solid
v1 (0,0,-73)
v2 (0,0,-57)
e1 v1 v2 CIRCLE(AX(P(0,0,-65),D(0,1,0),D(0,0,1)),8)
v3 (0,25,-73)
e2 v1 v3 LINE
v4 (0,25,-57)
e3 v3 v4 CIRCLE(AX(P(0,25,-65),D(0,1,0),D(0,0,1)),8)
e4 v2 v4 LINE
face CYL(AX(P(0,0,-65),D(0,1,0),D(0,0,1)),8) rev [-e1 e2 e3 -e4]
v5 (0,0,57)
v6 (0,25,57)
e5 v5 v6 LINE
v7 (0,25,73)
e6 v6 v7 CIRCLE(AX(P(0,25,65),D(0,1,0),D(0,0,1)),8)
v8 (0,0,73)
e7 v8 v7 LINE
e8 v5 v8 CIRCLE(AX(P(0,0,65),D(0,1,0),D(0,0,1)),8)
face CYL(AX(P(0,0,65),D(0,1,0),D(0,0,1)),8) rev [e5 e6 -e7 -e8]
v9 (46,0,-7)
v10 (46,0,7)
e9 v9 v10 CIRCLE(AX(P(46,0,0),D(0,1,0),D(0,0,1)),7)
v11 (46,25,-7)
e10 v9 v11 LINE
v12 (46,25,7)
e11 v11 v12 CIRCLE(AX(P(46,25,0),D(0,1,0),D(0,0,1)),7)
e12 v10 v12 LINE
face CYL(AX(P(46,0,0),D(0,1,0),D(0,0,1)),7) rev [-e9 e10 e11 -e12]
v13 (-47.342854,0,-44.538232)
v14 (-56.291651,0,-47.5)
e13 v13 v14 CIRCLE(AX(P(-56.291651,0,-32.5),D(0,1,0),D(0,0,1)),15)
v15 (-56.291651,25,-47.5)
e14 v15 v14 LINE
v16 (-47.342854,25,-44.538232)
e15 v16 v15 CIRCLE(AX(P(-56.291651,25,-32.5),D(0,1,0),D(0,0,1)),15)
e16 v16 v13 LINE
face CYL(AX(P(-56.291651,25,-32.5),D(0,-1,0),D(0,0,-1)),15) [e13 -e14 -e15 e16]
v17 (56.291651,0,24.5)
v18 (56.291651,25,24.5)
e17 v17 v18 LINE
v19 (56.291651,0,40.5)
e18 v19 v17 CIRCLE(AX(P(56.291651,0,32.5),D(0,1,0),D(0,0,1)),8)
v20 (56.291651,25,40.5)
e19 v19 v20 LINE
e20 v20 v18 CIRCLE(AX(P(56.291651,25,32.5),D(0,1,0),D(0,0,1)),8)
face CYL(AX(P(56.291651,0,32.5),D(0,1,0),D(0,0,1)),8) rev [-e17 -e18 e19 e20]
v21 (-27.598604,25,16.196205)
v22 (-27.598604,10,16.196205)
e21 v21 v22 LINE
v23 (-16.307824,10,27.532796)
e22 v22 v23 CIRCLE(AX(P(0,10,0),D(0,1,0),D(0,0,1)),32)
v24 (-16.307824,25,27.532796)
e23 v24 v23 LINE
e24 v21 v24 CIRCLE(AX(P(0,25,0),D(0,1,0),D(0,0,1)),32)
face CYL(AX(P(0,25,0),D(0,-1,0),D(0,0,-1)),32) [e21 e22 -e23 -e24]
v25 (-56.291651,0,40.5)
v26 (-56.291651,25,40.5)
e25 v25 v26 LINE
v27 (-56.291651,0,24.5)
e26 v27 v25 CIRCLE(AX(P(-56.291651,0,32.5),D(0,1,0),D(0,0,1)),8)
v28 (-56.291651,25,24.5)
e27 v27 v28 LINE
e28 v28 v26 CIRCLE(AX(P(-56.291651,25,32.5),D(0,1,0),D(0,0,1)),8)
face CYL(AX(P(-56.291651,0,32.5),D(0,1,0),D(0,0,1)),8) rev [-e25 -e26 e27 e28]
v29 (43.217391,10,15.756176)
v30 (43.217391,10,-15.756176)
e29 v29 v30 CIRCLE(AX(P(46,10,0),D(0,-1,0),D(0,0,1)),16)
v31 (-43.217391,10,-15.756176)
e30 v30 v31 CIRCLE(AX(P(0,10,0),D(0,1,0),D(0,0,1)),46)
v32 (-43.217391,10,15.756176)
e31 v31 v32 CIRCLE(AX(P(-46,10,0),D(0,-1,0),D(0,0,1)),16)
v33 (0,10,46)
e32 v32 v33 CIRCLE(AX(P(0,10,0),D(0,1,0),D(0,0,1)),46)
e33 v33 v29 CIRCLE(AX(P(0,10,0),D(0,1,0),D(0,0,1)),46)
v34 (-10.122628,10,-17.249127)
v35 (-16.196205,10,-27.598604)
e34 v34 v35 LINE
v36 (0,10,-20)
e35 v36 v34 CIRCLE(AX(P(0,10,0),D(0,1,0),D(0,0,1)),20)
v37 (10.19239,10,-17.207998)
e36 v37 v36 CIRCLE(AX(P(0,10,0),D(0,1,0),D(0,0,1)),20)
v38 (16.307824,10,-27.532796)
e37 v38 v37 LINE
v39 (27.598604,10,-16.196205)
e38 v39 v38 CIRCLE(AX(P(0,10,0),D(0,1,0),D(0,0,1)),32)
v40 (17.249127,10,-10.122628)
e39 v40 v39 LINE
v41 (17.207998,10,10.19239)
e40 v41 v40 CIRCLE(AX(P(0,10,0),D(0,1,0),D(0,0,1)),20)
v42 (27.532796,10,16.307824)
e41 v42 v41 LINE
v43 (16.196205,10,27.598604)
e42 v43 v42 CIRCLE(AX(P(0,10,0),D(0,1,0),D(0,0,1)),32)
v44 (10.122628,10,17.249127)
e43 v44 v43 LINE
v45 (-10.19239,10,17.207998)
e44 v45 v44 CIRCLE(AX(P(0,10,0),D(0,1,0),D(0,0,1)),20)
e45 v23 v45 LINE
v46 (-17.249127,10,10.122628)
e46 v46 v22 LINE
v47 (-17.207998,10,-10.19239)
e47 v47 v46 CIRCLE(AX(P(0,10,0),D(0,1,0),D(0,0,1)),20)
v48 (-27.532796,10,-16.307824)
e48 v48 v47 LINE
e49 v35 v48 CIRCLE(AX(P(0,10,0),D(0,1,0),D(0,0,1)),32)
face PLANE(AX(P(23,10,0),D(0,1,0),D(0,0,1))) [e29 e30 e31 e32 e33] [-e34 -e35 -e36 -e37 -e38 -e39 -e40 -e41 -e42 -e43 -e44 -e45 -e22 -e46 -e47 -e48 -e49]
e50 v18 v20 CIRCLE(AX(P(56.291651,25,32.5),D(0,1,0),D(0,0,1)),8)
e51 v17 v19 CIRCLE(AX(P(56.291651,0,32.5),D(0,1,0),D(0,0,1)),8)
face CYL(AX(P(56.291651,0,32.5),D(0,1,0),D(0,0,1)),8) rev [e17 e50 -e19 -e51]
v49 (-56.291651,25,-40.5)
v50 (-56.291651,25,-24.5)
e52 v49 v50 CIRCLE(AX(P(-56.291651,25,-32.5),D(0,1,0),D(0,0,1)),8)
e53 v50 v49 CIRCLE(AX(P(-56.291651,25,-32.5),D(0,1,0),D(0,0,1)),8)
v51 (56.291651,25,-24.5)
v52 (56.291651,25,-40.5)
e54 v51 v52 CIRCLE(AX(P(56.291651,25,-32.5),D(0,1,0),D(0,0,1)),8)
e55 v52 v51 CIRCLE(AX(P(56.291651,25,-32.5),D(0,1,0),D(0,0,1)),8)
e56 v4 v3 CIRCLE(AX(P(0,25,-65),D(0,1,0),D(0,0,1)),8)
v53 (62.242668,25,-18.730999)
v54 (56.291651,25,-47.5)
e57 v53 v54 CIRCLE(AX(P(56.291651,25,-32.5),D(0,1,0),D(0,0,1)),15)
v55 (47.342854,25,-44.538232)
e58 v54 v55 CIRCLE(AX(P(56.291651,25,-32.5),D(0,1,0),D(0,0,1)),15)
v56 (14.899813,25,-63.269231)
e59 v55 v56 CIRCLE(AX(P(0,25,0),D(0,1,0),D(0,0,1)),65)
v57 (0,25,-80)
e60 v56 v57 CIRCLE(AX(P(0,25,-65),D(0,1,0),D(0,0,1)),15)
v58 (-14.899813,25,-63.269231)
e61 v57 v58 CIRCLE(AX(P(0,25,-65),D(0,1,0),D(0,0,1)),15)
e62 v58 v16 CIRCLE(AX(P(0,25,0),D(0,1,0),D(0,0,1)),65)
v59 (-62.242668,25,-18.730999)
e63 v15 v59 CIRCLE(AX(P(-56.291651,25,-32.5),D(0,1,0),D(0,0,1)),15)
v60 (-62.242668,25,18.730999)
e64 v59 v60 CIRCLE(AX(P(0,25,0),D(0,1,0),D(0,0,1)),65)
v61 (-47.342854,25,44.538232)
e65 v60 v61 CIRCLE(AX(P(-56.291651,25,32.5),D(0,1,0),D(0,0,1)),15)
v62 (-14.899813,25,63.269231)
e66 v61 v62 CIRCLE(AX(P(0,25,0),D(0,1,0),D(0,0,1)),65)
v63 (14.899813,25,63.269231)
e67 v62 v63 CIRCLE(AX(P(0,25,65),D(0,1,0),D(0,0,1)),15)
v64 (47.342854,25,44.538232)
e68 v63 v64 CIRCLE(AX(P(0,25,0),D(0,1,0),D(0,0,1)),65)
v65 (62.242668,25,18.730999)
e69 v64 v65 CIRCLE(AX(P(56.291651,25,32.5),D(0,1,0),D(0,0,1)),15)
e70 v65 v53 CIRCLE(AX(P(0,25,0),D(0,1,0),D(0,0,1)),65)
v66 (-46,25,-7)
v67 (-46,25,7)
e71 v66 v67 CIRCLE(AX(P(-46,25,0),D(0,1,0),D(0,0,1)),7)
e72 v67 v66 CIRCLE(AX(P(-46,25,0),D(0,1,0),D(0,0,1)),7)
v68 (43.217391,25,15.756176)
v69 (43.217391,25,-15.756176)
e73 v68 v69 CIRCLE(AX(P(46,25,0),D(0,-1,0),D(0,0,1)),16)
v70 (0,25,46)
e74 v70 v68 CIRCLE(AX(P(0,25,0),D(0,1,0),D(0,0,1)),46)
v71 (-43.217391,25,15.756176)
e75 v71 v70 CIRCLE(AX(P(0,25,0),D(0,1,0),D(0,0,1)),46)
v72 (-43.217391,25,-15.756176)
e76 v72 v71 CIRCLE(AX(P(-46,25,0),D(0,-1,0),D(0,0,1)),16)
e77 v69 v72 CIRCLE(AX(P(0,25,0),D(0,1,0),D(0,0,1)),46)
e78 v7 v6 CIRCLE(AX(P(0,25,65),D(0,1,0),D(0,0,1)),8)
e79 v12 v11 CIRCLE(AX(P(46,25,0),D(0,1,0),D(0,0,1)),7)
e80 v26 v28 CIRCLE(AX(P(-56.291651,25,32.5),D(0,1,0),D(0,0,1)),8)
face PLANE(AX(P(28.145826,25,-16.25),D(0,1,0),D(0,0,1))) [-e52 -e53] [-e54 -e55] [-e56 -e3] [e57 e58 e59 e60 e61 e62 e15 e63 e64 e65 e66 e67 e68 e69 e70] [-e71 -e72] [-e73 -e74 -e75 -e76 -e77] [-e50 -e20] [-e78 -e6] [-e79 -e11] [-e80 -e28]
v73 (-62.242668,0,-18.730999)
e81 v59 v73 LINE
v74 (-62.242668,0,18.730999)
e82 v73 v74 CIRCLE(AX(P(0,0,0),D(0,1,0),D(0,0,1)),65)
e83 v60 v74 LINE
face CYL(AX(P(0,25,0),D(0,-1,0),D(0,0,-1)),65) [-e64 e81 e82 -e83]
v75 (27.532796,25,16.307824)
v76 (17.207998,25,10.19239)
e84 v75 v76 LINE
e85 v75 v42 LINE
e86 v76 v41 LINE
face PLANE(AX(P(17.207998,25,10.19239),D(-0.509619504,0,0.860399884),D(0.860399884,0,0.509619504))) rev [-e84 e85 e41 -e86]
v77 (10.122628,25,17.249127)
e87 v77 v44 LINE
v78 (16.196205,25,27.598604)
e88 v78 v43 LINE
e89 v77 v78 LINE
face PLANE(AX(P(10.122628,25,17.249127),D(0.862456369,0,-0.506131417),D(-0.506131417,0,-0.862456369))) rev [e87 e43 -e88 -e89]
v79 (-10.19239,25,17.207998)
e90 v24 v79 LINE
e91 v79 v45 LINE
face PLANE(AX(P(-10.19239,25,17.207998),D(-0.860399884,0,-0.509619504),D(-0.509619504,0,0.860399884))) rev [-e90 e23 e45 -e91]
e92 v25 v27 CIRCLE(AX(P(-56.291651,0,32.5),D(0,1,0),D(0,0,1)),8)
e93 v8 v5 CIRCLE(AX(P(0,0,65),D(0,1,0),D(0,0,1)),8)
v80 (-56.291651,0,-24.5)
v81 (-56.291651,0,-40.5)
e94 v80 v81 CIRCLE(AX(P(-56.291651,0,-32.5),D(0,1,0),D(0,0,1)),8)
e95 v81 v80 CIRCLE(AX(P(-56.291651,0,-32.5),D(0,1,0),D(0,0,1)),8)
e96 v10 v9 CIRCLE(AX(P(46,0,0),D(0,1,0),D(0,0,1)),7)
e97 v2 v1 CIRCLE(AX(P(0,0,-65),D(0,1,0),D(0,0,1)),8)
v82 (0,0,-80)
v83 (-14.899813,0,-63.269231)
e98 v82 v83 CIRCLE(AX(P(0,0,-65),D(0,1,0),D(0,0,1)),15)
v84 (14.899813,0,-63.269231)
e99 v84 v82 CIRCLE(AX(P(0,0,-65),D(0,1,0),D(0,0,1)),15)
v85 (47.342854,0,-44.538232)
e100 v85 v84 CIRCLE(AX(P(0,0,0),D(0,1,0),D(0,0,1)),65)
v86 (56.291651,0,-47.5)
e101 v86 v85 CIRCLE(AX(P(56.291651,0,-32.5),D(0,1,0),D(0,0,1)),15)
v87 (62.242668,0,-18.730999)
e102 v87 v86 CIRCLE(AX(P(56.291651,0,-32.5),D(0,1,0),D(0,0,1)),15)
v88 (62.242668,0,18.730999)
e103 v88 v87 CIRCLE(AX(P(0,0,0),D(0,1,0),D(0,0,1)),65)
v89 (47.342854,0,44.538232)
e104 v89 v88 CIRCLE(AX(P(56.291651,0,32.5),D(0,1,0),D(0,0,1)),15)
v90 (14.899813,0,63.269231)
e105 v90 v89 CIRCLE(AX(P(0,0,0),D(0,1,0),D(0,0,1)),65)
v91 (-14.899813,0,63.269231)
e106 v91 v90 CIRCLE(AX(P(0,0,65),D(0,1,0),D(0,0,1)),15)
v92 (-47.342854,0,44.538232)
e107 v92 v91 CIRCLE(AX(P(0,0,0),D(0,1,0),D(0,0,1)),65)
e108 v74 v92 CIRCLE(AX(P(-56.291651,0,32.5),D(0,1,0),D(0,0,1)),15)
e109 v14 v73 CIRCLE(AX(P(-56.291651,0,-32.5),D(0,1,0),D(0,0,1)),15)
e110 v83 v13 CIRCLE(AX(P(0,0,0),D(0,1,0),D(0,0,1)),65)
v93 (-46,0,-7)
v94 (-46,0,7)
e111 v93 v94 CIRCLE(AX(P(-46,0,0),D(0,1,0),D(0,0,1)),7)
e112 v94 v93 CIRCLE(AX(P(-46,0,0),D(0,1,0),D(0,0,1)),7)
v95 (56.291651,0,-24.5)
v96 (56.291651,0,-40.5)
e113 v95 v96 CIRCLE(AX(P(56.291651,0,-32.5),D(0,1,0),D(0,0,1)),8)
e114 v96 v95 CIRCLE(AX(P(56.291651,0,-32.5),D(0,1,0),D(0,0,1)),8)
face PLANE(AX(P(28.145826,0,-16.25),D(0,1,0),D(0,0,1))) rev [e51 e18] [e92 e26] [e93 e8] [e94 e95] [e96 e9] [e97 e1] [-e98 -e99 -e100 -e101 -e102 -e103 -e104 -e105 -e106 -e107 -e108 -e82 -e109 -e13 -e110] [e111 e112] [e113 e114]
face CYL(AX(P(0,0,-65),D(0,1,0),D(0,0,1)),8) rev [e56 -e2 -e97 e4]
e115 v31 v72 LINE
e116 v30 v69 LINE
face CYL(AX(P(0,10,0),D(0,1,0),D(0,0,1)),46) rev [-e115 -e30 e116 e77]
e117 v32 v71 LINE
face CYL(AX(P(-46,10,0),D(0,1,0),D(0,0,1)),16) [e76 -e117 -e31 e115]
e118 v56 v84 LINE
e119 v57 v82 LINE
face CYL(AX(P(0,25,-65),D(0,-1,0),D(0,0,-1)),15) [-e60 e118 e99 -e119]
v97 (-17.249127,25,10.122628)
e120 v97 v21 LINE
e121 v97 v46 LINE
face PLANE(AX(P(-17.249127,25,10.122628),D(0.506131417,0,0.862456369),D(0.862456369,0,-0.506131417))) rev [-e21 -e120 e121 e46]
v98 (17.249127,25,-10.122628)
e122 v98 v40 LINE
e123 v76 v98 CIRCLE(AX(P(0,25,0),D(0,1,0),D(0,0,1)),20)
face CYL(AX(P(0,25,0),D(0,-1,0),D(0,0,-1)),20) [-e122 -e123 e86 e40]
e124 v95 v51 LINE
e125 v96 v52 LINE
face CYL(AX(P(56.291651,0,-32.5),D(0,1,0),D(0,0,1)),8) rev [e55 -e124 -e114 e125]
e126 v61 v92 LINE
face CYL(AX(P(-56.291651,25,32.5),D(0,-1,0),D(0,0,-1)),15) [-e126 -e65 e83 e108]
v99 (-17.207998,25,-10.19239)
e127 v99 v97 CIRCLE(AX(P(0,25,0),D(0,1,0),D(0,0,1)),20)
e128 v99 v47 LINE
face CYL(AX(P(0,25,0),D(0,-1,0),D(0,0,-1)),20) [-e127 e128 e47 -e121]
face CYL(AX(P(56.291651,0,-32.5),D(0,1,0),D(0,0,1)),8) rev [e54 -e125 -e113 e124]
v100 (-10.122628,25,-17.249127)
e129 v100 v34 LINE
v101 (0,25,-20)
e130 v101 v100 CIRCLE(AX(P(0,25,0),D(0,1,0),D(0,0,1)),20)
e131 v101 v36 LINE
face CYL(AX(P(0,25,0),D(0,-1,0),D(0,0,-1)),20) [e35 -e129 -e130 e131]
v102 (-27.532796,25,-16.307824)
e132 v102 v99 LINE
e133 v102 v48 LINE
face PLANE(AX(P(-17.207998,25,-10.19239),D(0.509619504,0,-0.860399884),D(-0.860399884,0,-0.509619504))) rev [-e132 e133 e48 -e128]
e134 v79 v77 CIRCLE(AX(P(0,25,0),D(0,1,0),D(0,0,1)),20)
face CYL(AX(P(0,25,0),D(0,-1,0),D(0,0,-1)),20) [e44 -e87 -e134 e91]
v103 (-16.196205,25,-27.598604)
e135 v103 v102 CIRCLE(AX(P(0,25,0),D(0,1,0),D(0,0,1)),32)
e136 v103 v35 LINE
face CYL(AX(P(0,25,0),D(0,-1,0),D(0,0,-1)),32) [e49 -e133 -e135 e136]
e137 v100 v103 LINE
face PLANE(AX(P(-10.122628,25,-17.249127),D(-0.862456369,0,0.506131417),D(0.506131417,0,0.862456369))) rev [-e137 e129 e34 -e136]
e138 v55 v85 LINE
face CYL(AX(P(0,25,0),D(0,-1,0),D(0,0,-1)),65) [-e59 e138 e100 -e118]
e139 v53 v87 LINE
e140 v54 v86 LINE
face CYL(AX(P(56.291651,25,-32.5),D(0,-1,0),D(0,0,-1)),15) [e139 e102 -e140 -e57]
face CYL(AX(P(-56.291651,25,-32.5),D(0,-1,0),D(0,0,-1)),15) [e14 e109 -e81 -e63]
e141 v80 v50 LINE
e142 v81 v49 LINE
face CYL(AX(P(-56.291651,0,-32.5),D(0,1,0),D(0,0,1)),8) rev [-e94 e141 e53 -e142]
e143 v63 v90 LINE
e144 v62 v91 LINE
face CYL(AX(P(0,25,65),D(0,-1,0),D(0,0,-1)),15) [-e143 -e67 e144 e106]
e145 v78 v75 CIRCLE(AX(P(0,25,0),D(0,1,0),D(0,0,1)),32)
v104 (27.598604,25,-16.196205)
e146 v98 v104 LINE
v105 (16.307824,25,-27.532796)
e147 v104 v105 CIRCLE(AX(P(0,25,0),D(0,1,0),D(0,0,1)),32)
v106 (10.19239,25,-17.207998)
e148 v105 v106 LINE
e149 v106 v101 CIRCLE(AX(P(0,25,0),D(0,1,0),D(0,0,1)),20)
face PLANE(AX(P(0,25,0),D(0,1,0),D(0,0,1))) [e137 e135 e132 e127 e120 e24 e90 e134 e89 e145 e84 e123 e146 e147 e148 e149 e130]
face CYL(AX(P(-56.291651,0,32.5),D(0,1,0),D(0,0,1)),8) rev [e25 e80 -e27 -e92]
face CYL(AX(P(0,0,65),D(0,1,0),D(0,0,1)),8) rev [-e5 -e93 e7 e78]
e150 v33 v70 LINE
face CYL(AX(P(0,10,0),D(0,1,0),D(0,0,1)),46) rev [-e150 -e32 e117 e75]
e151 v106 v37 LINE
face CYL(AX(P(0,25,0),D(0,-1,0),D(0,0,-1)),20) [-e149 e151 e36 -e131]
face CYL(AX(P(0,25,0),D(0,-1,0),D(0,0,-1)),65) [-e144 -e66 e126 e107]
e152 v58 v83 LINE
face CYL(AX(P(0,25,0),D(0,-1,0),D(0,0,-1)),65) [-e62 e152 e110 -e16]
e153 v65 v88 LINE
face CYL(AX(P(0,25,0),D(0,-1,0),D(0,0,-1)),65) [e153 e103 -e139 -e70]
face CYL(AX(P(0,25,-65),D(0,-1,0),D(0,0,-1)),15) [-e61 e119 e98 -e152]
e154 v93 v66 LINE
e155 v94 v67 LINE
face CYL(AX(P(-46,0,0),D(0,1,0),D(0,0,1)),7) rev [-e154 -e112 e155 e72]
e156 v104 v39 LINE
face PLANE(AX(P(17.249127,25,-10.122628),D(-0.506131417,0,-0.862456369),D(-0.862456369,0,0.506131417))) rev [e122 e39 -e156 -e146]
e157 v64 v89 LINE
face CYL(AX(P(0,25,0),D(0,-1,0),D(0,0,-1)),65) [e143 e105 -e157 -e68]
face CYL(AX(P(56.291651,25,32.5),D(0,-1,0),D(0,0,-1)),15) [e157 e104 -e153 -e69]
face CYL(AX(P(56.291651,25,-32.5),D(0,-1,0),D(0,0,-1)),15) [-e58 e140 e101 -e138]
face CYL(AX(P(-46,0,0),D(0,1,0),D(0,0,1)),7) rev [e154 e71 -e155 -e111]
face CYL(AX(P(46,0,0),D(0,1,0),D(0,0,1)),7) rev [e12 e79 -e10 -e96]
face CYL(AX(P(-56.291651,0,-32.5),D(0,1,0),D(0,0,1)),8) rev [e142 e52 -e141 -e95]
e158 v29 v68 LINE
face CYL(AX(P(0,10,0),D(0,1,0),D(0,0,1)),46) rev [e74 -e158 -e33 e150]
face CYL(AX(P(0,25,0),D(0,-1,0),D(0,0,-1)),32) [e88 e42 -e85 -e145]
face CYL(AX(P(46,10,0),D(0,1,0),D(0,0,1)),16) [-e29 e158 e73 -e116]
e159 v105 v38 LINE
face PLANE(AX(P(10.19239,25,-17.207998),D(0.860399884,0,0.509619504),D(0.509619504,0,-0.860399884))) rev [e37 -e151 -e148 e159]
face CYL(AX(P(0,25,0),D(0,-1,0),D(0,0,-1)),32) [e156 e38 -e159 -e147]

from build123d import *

# Parameters (mm, degrees)
FLANGE_PLATE_DEPTH        = 25
BOLT_HOLES_SKETCH_R       = 8
BOLT_HOLES_6X_16_DEPTH    = 25
ANNULAR_RECESS_92_DEPTH   = 15
LUG_HOLES_SKETCH_R        = 7
LUG_HOLES_2X_14_DEPTH     = 111.034083526
KEYED_CENTRE_HUB_40_DEPTH = 15


with BuildPart() as part:
    # Flange Profile Sketch → Flange Plate (new body)
    with BuildSketch(Plane(origin=(0, 0, 0), x_dir=(1, 0, 0), z_dir=(0, 1, 0))):
        with BuildLine():
            ThreePointArc((-14.89981335, 63.269230769), (-32.5, 56.291651246), (-47.342854449, 44.538232258))
            ThreePointArc((-47.342854449, 44.538232258), (-69.282032303, 40), (-62.242667799, 18.730998512))
            ThreePointArc((-62.242667799, 18.730998512), (-65, 0), (-62.242667799, -18.730998512))
            ThreePointArc((-62.242667799, -18.730998512), (-69.282032303, -40), (-47.342854449, -44.538232258))
            ThreePointArc((-47.342854449, -44.538232258), (-32.5, -56.291651246), (-14.89981335, -63.269230769))
            ThreePointArc((-14.89981335, -63.269230769), (0, -80), (14.89981335, -63.269230769))
            ThreePointArc((14.89981335, -63.269230769), (32.5, -56.291651246), (47.342854449, -44.538232258))
            ThreePointArc((47.342854449, -44.538232258), (69.282032303, -40), (62.242667799, -18.730998512))
            ThreePointArc((62.242667799, -18.730998512), (65, 0), (62.242667799, 18.730998512))
            ThreePointArc((62.242667799, 18.730998512), (69.282032303, 40), (47.342854449, 44.538232258))
            ThreePointArc((47.342854449, 44.538232258), (32.5, 56.291651246), (14.89981335, 63.269230769))
            ThreePointArc((14.89981335, 63.269230769), (0, 80), (-14.89981335, 63.269230769))
        make_face()
    extrude(amount=FLANGE_PLATE_DEPTH)

    # Bolt Holes Sketch → Bolt Holes 6xØ16 (cut)
    with BuildSketch(Plane(origin=(0, 25, 0), x_dir=(1, 0, 0), z_dir=(0, 1, 0))):
        with Locations(Location((0, 65, 0), (0, 0, 270))):
            Circle(BOLT_HOLES_SKETCH_R)
        with Locations(Location((56.291651246, 32.5, 0), (0, 0, 270))):
            Circle(BOLT_HOLES_SKETCH_R)
        with Locations(Location((56.291651246, -32.5, 0), (0, 0, 270))):
            Circle(BOLT_HOLES_SKETCH_R)
        with Locations(Location((0, -65, 0), (0, 0, 270))):
            Circle(BOLT_HOLES_SKETCH_R)
        with Locations(Location((-56.291651246, -32.5, 0), (0, 0, 270))):
            Circle(BOLT_HOLES_SKETCH_R)
        with Locations(Location((-56.291651246, 32.5, 0), (0, 0, 270))):
            Circle(BOLT_HOLES_SKETCH_R)
    extrude(amount=-BOLT_HOLES_6X_16_DEPTH, mode=Mode.SUBTRACT)

    # Recess Sketch → Annular Recess Ø92 (cut)
    with BuildSketch(Plane(origin=(0, 25, 0), x_dir=(1, 0, 0), z_dir=(0, 1, 0))):
        with BuildLine():
            ThreePointArc((-43.217391304, -15.756176213), (0, -46), (43.217391304, -15.756176213))
            ThreePointArc((43.217391304, -15.756176213), (30, 0), (43.217391304, 15.756176213))
            ThreePointArc((43.217391304, 15.756176213), (0, 46), (-43.217391304, 15.756176213))
            ThreePointArc((-43.217391304, 15.756176213), (-30, 0), (-43.217391304, -15.756176213))
        make_face()
    extrude(amount=-ANNULAR_RECESS_92_DEPTH, mode=Mode.SUBTRACT)

    # Lug Holes Sketch → Lug Holes 2xØ14 (cut, through all)
    with BuildSketch(Plane(origin=(0, 25, 0), x_dir=(1, 0, 0), z_dir=(0, 1, 0))):
        with Locations(Location((-46, 0, 0), (0, 0, 270))):
            Circle(LUG_HOLES_SKETCH_R)
        with Locations(Location((46, 0, 0), (0, 0, 270))):
            Circle(LUG_HOLES_SKETCH_R)
    extrude(amount=-LUG_HOLES_2X_14_DEPTH, mode=Mode.SUBTRACT)

    # Centre Hub Sketch → Keyed Centre Hub Ø40 (add)
    with BuildSketch(Plane(origin=(0, 10, 0), x_dir=(1, 0, 0), z_dir=(0, 1, 0))):
        with BuildLine():
            Line((17.207997686, -10.192390085), (27.532796297, -16.307824137))
            ThreePointArc((27.532796297, -16.307824137), (22.581559349, -22.673181898), (16.196205348, -27.598603811))
            Line((16.196205348, -27.598603811), (10.122628343, -17.249127382))
            ThreePointArc((10.122628343, -17.249127382), (-0.040491828, -19.99995901), (-10.192390085, -17.207997686))
            Line((-10.192390085, -17.207997686), (-16.307824137, -27.532796297))
            ThreePointArc((-16.307824137, -27.532796297), (-22.673181898, -22.581559349), (-27.598603811, -16.196205348))
            Line((-27.598603811, -16.196205348), (-17.249127382, -10.122628343))
            ThreePointArc((-17.249127382, -10.122628343), (-19.99995901, 0.040491828), (-17.207997686, 10.192390085))
            Line((-17.207997686, 10.192390085), (-27.532796297, 16.307824137))
            ThreePointArc((-27.532796297, 16.307824137), (-22.581559349, 22.673181898), (-16.196205348, 27.598603811))
            Line((-16.196205348, 27.598603811), (-10.122628343, 17.249127382))
            ThreePointArc((-10.122628343, 17.249127382), (0.040491828, 19.99995901), (10.192390085, 17.207997686))
            Line((10.192390085, 17.207997686), (16.307824137, 27.532796297))
            ThreePointArc((16.307824137, 27.532796297), (22.673181898, 22.581559349), (27.598603811, 16.196205348))
            Line((27.598603811, 16.196205348), (17.249127382, 10.122628343))
            ThreePointArc((17.249127382, 10.122628343), (19.99995901, -0.040491828), (17.207997686, -10.192390085))
        make_face()
    extrude(amount=KEYED_CENTRE_HUB_40_DEPTH)


solid = part.part
